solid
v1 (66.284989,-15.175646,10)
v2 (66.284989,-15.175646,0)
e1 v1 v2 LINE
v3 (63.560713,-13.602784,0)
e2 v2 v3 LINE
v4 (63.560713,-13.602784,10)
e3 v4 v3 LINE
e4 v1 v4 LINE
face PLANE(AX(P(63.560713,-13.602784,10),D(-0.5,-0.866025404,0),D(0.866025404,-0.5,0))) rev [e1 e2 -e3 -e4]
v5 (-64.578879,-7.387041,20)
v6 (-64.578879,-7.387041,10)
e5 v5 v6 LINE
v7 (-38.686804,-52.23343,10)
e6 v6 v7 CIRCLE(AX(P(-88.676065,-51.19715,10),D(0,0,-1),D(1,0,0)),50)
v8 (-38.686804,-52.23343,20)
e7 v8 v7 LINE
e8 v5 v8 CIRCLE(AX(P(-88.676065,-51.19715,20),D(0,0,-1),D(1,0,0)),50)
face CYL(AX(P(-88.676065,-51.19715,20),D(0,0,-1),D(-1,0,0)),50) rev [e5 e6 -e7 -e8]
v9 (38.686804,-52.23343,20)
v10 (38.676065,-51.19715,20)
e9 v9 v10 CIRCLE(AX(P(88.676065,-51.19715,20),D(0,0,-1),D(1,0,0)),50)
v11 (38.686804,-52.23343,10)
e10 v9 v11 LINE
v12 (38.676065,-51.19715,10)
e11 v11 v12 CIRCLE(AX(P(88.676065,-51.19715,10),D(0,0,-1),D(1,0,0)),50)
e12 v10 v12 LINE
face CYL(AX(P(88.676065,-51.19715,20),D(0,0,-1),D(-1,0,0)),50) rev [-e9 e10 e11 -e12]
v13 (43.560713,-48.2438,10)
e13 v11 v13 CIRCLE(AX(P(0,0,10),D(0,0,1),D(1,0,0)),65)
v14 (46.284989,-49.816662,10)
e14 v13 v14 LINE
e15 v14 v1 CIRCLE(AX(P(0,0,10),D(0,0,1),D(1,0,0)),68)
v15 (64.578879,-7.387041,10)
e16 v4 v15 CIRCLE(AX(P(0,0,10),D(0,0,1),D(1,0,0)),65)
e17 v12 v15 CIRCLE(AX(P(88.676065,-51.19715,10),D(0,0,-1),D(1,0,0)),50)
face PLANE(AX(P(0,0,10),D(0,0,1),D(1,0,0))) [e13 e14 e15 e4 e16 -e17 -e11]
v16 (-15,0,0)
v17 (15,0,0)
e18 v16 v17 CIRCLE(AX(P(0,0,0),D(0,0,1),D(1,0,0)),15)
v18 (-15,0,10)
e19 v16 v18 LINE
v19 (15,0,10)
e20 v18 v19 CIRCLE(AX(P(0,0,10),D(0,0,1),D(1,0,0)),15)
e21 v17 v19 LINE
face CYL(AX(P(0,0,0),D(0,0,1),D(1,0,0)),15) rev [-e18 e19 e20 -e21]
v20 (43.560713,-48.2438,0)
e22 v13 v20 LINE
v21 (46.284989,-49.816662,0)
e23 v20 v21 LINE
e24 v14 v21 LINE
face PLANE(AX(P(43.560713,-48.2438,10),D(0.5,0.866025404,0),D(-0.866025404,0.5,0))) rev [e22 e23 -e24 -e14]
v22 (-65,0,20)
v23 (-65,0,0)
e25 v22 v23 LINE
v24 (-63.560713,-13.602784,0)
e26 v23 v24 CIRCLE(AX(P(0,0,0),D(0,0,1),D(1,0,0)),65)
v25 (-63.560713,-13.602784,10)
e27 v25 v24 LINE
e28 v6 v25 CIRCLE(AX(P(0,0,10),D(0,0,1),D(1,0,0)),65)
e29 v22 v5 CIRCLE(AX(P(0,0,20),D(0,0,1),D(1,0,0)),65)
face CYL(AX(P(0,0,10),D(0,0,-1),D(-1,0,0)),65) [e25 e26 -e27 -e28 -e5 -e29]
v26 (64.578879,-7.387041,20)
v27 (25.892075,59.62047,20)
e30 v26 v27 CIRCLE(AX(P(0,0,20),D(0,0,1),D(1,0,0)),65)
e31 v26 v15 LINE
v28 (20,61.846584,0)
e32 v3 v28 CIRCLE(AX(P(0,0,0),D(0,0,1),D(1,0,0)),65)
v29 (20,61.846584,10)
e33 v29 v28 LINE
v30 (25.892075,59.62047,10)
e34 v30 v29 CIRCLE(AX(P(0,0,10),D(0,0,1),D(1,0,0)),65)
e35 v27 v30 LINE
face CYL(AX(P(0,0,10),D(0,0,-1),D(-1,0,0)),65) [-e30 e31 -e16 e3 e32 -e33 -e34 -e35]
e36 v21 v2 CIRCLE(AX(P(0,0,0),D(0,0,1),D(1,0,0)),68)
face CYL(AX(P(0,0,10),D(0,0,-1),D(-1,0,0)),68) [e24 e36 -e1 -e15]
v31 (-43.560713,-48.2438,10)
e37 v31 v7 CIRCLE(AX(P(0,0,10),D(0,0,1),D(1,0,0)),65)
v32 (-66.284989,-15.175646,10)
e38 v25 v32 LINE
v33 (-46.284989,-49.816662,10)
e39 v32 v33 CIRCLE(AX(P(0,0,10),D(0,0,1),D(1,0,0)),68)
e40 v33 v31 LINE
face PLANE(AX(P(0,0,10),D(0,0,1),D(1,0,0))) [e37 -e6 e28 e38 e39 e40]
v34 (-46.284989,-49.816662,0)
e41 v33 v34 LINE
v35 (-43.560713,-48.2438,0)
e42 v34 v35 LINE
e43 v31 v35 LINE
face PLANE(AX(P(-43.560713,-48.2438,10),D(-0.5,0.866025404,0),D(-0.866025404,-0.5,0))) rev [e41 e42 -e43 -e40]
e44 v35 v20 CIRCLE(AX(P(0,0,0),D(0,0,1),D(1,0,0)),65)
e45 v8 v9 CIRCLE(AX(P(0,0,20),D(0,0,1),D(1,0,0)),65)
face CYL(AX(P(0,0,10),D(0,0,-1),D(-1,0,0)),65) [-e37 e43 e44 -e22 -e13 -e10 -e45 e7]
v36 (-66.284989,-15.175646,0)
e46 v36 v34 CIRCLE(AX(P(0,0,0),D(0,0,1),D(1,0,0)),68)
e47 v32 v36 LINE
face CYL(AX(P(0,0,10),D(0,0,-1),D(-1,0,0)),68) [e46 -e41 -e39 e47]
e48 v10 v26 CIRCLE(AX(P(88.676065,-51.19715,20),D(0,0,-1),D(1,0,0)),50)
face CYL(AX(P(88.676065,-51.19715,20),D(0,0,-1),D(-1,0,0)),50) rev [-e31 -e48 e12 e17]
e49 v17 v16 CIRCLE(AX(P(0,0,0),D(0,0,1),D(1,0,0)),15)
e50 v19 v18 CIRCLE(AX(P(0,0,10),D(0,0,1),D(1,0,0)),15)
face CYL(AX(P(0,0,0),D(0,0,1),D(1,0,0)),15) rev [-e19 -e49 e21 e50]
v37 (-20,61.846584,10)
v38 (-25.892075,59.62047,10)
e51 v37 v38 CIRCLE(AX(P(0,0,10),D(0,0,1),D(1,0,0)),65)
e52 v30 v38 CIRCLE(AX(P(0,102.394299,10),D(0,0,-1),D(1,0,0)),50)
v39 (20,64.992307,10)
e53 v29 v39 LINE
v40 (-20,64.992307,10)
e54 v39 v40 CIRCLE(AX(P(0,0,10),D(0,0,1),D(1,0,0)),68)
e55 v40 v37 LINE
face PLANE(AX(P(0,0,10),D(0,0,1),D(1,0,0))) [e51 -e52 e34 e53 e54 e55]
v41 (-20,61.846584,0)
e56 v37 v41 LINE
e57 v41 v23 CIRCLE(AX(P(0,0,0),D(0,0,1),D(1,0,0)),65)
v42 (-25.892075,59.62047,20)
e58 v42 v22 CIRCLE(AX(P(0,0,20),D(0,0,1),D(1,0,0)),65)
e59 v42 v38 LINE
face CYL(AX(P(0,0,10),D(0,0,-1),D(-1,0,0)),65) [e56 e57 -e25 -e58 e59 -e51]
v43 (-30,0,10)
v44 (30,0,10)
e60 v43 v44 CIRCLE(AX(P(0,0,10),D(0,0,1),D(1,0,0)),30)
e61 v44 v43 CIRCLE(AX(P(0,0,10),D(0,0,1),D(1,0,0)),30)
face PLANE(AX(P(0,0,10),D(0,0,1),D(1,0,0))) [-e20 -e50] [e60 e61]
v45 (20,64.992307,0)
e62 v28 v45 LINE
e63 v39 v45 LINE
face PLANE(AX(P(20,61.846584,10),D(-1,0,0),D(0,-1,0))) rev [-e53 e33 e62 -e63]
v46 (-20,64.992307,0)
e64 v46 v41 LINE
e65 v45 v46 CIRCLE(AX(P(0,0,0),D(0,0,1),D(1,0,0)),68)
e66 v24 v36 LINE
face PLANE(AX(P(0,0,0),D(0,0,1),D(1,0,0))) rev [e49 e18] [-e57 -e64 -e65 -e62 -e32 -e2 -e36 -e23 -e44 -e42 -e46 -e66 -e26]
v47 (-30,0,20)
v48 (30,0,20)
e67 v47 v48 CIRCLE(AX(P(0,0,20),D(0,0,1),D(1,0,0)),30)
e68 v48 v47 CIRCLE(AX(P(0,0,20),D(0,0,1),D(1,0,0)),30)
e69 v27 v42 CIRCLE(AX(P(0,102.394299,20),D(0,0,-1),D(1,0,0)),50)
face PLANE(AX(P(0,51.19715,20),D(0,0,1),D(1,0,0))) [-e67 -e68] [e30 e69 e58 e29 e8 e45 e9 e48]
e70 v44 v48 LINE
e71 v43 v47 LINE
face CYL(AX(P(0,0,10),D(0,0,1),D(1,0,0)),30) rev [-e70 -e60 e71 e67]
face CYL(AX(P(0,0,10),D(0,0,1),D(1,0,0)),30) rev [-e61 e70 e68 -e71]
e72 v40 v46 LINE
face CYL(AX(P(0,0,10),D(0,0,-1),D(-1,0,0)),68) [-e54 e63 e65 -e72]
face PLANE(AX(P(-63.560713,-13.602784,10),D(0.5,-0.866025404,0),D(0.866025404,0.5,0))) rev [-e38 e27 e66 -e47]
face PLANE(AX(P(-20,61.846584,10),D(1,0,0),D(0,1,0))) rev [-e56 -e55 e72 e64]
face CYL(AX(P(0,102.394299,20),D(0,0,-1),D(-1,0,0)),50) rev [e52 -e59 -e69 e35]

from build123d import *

# Parameters (mm, degrees)
BASE_DISC_DEPTH       = 10
UPPER_SECTION_DEPTH   = 10
COUNTERBORE_SKETCH_R  = 30
COUNTERBORE_DEPTH     = 10
THROUGH_BORE_SKETCH_R = 15
THROUGH_BORE_DEPTH    = 10


with BuildPart() as part:
    # Base Disc Profile Sketch → Base Disc (new body)
    with BuildSketch(Plane.XY):
        with BuildLine():
            Line((20, 61.846584384), (20, 64.992307237))
            ThreePointArc((20, 64.992307237), (0, 68), (-20, 64.992307237))
            Line((-20, 64.992307237), (-20, 61.846584384))
            ThreePointArc((-20, 61.846584384), (-56.291651246, 32.5), (-63.560713214, -13.602784116))
            Line((-63.560713214, -13.602784116), (-66.284989118, -15.175645543))
            ThreePointArc((-66.284989118, -15.175645543), (-58.889727457, -34), (-46.284989118, -49.816661694))
            Line((-46.284989118, -49.816661694), (-43.560713214, -48.243800268))
            ThreePointArc((-43.560713214, -48.243800268), (0, -65), (43.560713214, -48.243800268))
            Line((43.560713214, -48.243800268), (46.284989118, -49.816661694))
            ThreePointArc((46.284989118, -49.816661694), (58.889727457, -34), (66.284989118, -15.175645543))
            Line((66.284989118, -15.175645543), (63.560713214, -13.602784116))
            ThreePointArc((63.560713214, -13.602784116), (56.291651246, 32.5), (20, 61.846584384))
        make_face()
    extrude(amount=BASE_DISC_DEPTH)

    # Upper Section Sketch → Upper Section (add)
    with BuildSketch(Plane.XY.offset(10)):
        with BuildLine():
            ThreePointArc((-25.892074701, 59.620470207), (-56.291651246, 32.5), (-64.578879135, -7.387040655))
            ThreePointArc((-64.578879135, -7.387040655), (-45.374794332, -26.197149722), (-38.686804434, -52.233429551))
            ThreePointArc((-38.686804434, -52.233429551), (0, -65), (38.686804434, -52.233429551))
            ThreePointArc((38.686804434, -52.233429551), (45.374794332, -26.197149722), (64.578879135, -7.387040655))
            ThreePointArc((64.578879135, -7.387040655), (56.291651246, 32.5), (25.892074701, 59.620470207))
            ThreePointArc((25.892074701, 59.620470207), (0, 52.394299444), (-25.892074701, 59.620470207))
        make_face()
    extrude(amount=UPPER_SECTION_DEPTH)

    # Counterbore Sketch → Counterbore (cut)
    with BuildSketch(Plane.XY.offset(20)):
        Circle(COUNTERBORE_SKETCH_R)
    extrude(amount=-COUNTERBORE_DEPTH, mode=Mode.SUBTRACT)

    # Through Bore Sketch → Through Bore (cut)
    with BuildSketch(Plane.XY.offset(10)):
        Circle(THROUGH_BORE_SKETCH_R)
    extrude(amount=-THROUGH_BORE_DEPTH, mode=Mode.SUBTRACT)


solid = part.part
